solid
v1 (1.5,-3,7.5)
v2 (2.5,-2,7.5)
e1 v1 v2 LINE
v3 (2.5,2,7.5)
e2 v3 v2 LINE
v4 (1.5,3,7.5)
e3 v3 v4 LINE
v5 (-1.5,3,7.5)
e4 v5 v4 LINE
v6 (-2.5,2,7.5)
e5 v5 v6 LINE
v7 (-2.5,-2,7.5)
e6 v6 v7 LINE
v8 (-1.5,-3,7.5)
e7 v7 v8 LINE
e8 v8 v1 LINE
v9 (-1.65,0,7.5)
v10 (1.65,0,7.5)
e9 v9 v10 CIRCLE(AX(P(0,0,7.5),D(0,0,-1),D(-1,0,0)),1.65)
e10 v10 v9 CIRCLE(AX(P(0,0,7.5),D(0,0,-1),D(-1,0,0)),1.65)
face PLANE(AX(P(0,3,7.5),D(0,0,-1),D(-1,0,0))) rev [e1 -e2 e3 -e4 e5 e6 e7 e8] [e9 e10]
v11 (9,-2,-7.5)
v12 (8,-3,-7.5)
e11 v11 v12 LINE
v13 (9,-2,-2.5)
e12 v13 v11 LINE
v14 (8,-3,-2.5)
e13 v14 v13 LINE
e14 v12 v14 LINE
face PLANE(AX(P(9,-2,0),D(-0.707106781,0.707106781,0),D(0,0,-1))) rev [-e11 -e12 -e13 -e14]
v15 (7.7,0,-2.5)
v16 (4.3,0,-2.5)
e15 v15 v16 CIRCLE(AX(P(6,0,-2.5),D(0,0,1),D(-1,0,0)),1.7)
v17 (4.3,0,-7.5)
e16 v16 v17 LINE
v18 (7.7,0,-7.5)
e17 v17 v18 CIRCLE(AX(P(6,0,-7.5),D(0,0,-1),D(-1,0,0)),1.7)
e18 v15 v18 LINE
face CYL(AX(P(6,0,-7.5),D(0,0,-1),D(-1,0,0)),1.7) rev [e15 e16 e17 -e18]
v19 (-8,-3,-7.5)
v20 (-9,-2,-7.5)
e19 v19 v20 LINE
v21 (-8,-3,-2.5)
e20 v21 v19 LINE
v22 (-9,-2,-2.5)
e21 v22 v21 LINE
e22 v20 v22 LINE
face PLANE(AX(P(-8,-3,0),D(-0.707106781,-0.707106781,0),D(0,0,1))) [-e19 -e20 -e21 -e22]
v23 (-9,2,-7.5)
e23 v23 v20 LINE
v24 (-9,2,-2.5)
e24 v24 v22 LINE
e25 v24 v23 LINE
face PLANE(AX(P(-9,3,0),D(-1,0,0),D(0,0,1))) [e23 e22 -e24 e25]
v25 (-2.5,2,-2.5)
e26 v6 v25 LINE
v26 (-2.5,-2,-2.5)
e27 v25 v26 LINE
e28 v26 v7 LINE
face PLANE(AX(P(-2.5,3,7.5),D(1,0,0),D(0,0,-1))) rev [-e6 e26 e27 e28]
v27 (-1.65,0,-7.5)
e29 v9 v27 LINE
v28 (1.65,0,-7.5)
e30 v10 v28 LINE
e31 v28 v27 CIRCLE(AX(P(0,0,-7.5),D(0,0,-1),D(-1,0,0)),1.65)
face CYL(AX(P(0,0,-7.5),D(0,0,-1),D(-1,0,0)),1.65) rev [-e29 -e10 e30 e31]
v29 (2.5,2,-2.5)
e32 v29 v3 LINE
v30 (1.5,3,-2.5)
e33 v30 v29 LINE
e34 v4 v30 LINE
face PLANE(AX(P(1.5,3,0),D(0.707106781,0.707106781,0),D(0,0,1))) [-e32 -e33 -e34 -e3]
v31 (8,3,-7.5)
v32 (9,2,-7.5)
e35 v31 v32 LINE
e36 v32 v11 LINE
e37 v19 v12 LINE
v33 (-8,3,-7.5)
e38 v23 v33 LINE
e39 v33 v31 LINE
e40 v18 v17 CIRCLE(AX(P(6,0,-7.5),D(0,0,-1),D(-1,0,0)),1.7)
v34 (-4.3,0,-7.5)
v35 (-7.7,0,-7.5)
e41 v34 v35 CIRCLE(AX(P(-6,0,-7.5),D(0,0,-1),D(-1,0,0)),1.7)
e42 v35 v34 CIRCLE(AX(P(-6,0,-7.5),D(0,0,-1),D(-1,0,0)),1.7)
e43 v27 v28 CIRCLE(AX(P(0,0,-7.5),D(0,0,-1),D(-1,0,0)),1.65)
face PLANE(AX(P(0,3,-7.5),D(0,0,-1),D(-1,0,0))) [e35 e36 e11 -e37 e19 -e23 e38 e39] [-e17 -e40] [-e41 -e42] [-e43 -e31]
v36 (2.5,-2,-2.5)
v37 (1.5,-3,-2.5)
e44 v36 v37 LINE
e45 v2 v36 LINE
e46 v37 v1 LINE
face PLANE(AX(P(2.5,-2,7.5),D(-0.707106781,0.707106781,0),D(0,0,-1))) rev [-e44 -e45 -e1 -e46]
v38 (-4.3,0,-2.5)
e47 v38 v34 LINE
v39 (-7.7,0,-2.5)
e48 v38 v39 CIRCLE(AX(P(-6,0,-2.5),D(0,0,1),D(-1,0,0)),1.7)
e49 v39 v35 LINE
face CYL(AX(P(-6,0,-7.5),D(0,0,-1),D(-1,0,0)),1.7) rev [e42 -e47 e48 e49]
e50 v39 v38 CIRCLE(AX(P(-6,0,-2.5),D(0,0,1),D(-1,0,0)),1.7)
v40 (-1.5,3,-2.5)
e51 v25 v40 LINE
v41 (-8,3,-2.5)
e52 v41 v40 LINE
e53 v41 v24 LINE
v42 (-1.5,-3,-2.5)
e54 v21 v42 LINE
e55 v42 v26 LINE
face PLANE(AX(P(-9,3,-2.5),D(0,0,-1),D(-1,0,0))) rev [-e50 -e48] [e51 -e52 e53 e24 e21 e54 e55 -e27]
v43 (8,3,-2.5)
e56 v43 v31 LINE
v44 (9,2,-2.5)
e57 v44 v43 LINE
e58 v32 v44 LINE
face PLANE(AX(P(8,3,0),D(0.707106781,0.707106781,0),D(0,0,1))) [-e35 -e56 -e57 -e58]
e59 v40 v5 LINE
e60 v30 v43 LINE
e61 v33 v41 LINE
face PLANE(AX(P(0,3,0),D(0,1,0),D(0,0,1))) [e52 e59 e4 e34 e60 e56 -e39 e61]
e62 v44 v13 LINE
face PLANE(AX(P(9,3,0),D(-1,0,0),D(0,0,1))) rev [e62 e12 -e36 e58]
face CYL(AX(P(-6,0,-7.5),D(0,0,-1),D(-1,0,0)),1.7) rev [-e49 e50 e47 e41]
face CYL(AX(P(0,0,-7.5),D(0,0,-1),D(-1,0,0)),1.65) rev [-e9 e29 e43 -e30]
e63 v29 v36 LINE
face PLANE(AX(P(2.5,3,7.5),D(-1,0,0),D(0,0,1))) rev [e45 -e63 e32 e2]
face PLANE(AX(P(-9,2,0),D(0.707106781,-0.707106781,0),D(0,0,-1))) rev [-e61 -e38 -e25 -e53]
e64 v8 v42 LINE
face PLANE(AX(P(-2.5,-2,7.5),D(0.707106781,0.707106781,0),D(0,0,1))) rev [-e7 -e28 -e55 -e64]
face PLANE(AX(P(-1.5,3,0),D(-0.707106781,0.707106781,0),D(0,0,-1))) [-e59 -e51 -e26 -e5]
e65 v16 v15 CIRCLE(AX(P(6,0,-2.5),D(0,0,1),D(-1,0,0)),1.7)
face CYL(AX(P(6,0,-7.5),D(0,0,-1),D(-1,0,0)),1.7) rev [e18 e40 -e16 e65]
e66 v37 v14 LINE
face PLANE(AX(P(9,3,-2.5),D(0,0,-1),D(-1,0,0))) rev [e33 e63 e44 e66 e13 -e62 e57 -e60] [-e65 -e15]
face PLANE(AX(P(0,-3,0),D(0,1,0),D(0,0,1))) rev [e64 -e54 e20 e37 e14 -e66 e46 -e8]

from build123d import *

# Parameters (mm, degrees)
SKETCH3_W            = 18
SKETCH3_H            = 15
BOSS_EXTRUDE2_DEPTH  = 3
M3_CLEARANCE_HOLE1_D = 3.4
CHAMFER1_SIZE        = 1
SKETCH10_W           = 6.5
SKETCH10_H           = 10
CUT_EXTRUDE1_DEPTH   = 14.162446581
M4_TAPPED_HOLE1_D    = 3.3
CHAMFER2_SIZE        = 1


with BuildPart() as part:
    # Sketch3 → Boss-Extrude2 (new, symmetric)
    with BuildSketch(Plane(origin=(0, 0, 0), x_dir=(1, 0, 0), z_dir=(0, 1, 0))):
        Rectangle(SKETCH3_W, SKETCH3_H)
    extrude(amount=BOSS_EXTRUDE2_DEPTH, both=True)

    # M3 Clearance Hole1 (through all)
    with Locations(Plane(origin=(0, 0, -7.5), x_dir=(-1, 0, 0), z_dir=(0, 0, -1))):
        with Locations((-6, 0), (6, 0)):
            Hole(M3_CLEARANCE_HOLE1_D / 2)

    # Chamfer1
    chamfer1_edges = [part.edges().sort_by_distance(p)[0] for p in [
        (-9, 3, 0),
        (-9, -3, 0),
        (9, -3, 0),
        (9, 3, 0),
    ]]
    chamfer(chamfer1_edges, length=CHAMFER1_SIZE)

    # Sketch10 → Cut-Extrude1 (cut, through all)
    with BuildSketch(Plane(origin=(0, -3, 0), x_dir=(-1, 0, 0), z_dir=(0, -1, 0))):
        with Locations((-5.75, -2.5)):
            Rectangle(SKETCH10_W, SKETCH10_H)
        with Locations((5.75, -2.5)):
            Rectangle(SKETCH10_W, SKETCH10_H)
    extrude(amount=-CUT_EXTRUDE1_DEPTH, mode=Mode.SUBTRACT)

    # M4 Tapped Hole1 (through all)
    with Locations(Plane(origin=(0, 0, -7.5), x_dir=(-1, 0, 0), z_dir=(0, 0, -1))):
        with Locations((0, 0)):
            Hole(M4_TAPPED_HOLE1_D / 2)

    # Chamfer2
    chamfer2_edges = [part.edges().sort_by_distance(p)[0] for p in [
        (2.5, 3, 2.5),
        (2.5, -3, 2.5),
        (-2.5, 3, 2.5),
        (-2.5, -3, 2.5),
    ]]
    chamfer(chamfer2_edges, length=CHAMFER2_SIZE)


solid = part.part
